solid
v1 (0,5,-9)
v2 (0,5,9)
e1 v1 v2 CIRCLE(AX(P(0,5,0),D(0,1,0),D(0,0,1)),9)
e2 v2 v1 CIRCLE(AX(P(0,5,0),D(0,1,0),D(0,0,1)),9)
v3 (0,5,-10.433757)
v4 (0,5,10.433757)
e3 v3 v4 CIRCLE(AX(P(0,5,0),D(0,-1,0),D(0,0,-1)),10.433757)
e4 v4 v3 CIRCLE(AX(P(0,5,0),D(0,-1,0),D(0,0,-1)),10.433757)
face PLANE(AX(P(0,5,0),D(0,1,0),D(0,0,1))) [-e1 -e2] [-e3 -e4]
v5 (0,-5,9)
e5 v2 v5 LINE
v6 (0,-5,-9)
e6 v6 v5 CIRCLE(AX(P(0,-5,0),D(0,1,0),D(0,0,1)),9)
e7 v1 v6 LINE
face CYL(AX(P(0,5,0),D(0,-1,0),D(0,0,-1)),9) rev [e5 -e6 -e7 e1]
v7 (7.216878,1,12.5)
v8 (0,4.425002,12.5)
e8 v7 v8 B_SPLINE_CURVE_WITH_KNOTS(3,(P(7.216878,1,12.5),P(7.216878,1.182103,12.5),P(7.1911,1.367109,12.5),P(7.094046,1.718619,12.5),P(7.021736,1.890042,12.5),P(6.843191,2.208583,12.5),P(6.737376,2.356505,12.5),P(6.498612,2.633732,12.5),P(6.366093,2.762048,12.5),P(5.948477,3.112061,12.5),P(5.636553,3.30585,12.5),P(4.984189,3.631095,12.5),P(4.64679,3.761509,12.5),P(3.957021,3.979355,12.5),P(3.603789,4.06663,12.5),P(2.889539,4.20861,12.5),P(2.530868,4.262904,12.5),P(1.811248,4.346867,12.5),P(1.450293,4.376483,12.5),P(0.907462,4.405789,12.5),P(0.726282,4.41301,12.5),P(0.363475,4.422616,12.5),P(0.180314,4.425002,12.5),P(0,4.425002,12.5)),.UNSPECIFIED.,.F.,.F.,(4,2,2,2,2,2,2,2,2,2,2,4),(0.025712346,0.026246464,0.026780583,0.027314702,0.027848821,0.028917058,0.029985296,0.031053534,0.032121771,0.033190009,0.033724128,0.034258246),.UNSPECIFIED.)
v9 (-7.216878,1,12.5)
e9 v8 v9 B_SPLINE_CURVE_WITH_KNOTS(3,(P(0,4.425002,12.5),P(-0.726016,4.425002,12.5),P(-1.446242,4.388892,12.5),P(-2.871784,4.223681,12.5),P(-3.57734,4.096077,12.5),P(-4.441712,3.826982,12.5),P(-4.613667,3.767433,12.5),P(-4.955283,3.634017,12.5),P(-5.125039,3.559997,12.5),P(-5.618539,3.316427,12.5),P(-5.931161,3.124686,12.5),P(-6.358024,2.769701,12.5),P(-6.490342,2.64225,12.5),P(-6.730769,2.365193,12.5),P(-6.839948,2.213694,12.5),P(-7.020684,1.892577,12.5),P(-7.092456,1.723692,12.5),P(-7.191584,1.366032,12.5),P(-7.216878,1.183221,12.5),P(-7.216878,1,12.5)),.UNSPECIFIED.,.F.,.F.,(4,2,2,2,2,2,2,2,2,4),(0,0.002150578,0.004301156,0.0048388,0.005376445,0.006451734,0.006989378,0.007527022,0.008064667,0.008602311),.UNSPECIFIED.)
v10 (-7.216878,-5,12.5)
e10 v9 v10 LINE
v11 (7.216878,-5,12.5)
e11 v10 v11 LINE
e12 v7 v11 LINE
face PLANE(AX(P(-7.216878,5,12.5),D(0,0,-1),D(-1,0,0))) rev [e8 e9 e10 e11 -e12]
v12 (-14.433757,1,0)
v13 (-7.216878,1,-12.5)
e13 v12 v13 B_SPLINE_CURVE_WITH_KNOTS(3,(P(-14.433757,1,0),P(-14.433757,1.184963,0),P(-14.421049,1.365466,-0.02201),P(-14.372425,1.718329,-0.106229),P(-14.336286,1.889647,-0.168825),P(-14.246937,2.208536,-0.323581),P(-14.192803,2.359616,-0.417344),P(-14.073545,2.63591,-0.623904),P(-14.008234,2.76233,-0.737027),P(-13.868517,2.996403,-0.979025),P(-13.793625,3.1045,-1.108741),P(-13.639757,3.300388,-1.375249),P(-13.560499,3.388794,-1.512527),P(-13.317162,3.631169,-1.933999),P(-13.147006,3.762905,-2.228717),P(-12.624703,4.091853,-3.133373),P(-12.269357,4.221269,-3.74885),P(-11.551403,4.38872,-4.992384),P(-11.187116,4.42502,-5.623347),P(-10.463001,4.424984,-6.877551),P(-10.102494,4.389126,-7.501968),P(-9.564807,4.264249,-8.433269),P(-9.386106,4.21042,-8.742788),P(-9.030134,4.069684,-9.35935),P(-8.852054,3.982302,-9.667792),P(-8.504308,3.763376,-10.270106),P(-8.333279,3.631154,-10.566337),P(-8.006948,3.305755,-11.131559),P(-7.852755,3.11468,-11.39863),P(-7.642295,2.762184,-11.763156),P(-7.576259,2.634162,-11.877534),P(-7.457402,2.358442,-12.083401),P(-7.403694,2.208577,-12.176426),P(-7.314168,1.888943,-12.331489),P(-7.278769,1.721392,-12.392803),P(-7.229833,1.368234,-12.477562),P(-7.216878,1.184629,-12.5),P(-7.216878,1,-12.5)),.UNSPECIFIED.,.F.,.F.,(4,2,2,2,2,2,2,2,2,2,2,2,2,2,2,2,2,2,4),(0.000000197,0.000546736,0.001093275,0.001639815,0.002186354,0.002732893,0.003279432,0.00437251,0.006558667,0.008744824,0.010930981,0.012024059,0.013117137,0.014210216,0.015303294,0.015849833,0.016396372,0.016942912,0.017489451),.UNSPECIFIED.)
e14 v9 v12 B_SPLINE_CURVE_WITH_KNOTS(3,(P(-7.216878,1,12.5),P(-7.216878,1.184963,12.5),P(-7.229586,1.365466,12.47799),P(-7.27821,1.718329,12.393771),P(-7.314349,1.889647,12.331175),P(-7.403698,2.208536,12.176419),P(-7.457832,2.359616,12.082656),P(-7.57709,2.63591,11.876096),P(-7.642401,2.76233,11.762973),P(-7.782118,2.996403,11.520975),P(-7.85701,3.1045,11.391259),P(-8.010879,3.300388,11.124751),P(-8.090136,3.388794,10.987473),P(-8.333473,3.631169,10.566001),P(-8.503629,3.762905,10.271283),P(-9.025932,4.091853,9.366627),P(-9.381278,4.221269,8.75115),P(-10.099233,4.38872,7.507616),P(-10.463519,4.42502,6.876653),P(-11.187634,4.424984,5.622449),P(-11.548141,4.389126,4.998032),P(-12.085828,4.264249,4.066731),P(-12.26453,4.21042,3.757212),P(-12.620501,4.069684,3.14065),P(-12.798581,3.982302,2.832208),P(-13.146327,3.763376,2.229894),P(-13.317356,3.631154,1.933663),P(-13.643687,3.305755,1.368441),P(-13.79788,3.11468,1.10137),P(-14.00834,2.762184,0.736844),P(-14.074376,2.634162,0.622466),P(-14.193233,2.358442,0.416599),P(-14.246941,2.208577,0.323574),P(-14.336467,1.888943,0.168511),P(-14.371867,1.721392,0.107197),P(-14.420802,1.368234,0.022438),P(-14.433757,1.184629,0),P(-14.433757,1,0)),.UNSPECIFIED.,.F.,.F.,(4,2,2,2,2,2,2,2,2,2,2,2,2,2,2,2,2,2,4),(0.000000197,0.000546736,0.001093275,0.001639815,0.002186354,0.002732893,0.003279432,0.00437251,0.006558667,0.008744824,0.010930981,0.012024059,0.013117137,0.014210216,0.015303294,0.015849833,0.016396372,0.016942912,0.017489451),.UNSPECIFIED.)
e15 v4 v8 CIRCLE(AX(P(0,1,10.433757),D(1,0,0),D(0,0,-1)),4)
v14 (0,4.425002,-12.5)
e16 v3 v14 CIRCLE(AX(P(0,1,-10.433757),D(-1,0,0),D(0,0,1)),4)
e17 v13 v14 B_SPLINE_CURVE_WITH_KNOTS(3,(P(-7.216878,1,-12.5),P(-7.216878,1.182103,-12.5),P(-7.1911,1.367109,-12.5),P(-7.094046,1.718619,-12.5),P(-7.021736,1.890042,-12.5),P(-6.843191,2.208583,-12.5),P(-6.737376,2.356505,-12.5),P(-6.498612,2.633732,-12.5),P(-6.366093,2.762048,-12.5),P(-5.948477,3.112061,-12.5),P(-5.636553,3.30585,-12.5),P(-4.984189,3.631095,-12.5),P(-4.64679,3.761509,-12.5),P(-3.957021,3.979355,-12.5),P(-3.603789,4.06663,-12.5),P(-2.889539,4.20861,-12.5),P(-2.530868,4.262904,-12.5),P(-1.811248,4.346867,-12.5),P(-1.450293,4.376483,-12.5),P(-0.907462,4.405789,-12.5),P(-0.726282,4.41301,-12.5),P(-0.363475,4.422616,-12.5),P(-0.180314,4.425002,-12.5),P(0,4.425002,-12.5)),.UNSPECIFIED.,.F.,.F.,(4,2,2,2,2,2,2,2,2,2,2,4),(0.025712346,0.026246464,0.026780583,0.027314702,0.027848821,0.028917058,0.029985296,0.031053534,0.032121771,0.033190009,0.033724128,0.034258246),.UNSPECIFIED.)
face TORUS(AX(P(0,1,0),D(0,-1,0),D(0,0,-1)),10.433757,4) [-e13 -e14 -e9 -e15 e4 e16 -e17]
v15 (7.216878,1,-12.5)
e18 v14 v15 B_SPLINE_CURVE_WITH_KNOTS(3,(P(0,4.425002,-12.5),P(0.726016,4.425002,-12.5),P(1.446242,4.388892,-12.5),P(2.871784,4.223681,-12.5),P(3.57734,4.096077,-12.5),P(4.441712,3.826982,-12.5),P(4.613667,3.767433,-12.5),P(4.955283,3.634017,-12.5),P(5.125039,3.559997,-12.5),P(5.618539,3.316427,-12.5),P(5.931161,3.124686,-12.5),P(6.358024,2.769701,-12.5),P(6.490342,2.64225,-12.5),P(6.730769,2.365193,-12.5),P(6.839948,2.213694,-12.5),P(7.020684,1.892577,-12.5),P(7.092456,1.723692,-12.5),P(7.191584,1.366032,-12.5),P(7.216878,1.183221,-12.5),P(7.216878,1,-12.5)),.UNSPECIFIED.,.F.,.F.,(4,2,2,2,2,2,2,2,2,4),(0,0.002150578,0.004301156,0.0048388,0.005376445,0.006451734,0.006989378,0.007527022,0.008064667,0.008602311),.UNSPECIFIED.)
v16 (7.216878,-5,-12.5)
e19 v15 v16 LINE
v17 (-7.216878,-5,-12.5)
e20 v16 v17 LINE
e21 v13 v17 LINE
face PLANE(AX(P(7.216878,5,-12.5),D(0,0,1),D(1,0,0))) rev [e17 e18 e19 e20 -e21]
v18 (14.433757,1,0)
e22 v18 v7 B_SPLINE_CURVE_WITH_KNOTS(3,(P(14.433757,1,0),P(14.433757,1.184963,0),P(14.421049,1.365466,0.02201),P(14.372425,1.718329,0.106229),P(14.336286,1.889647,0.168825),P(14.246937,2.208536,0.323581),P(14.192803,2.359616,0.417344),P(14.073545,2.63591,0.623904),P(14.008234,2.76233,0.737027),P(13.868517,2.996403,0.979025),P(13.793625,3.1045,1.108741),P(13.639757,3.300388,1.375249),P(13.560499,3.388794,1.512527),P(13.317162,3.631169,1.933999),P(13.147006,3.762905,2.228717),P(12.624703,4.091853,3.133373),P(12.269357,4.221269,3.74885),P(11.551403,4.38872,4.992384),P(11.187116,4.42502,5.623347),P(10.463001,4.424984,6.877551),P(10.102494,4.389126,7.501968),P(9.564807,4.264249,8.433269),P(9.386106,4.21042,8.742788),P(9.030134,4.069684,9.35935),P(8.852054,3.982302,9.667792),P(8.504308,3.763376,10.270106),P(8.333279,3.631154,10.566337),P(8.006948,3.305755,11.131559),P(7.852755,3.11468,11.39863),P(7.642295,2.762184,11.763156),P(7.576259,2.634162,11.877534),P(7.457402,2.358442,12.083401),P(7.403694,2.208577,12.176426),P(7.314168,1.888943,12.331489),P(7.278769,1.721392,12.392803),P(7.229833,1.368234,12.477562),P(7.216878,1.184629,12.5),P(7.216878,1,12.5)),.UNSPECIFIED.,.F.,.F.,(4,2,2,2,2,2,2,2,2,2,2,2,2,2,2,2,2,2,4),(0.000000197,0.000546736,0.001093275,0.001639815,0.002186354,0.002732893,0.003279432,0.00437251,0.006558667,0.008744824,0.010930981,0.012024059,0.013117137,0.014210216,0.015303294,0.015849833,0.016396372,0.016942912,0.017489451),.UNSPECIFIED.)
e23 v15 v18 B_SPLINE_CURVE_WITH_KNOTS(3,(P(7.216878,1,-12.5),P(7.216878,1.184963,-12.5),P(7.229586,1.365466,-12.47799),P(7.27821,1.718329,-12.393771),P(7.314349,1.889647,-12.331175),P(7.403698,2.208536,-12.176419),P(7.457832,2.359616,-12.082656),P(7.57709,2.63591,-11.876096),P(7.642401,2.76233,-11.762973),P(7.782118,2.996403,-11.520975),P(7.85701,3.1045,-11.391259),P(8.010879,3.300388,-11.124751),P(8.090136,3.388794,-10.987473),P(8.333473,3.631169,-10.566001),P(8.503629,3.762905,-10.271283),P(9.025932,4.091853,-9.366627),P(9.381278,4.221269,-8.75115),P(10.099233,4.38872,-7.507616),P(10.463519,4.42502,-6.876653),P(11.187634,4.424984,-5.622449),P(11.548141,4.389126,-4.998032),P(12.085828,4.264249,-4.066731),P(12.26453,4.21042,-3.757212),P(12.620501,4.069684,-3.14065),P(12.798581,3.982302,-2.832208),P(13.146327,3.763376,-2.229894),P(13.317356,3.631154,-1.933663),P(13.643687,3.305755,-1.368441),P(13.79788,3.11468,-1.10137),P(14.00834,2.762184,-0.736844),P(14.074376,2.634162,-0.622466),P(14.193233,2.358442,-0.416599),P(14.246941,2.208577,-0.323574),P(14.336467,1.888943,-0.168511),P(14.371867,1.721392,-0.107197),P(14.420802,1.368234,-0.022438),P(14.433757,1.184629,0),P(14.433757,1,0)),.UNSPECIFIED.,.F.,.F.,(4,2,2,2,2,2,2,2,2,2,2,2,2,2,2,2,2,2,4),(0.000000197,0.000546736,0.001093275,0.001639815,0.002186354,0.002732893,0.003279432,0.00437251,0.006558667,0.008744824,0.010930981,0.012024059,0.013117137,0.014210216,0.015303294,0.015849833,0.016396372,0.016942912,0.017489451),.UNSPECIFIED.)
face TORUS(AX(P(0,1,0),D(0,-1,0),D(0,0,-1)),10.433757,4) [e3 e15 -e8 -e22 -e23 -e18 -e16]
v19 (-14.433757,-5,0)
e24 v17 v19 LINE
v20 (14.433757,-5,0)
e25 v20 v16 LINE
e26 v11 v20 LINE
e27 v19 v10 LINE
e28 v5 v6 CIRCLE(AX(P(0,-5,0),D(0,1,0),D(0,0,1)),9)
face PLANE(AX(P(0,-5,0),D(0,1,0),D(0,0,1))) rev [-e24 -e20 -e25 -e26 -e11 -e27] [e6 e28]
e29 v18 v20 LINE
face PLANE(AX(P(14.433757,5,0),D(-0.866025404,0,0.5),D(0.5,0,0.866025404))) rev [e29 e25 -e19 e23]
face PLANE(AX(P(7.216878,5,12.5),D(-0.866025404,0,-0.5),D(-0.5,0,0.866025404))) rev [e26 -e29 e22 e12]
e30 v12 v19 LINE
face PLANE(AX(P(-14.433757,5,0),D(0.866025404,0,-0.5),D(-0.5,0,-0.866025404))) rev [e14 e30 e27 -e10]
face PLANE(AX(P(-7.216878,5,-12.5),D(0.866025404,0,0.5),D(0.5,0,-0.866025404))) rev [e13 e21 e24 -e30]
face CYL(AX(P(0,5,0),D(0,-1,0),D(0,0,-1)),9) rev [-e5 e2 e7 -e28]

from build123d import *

# Parameters (mm, degrees)
HEX_PROFILE_SKETCH_R = 9
HEX_NUT_BODY_DEPTH   = 5


with BuildPart() as part:
    # Hex Profile Sketch → Hex Nut Body (new, symmetric)
    with BuildSketch(Plane(origin=(0, 0, 0), x_dir=(1, 0, 0), z_dir=(0, 1, 0))):
        Polygon((14.43375673, 0), (7.216878365, 12.5), (-7.216878365, 12.5), (-14.43375673, 0), (-7.216878365, -12.5), (7.216878365, -12.5), align=None)
        with Locations(Location((0, 0, 0), (0, 0, 270))):
            Circle(HEX_PROFILE_SKETCH_R, mode=Mode.SUBTRACT)
    extrude(amount=HEX_NUT_BODY_DEPTH, both=True)

    # Chamfer Profile Sketch → Nut Chamfer Cut (revolve, cut)
    with BuildSketch(Plane.XY, mode=Mode.PRIVATE) as nut_chamfer_cut_sk:
        with BuildLine():
            Line((10.43375673, 5), (14.43375673, 5))
            Line((14.43375673, 5), (14.43375673, 1))
            ThreePointArc((14.43375673, 1), (13.262183854, 3.828427125), (10.43375673, 5))
        make_face()
    revolve(nut_chamfer_cut_sk.sketch.rotate(Axis((0, 0, 0), (0, 1, 0)), 90), axis=Axis((0, 0, 0), (0, 1, 0)), mode=Mode.SUBTRACT)


solid = part.part
